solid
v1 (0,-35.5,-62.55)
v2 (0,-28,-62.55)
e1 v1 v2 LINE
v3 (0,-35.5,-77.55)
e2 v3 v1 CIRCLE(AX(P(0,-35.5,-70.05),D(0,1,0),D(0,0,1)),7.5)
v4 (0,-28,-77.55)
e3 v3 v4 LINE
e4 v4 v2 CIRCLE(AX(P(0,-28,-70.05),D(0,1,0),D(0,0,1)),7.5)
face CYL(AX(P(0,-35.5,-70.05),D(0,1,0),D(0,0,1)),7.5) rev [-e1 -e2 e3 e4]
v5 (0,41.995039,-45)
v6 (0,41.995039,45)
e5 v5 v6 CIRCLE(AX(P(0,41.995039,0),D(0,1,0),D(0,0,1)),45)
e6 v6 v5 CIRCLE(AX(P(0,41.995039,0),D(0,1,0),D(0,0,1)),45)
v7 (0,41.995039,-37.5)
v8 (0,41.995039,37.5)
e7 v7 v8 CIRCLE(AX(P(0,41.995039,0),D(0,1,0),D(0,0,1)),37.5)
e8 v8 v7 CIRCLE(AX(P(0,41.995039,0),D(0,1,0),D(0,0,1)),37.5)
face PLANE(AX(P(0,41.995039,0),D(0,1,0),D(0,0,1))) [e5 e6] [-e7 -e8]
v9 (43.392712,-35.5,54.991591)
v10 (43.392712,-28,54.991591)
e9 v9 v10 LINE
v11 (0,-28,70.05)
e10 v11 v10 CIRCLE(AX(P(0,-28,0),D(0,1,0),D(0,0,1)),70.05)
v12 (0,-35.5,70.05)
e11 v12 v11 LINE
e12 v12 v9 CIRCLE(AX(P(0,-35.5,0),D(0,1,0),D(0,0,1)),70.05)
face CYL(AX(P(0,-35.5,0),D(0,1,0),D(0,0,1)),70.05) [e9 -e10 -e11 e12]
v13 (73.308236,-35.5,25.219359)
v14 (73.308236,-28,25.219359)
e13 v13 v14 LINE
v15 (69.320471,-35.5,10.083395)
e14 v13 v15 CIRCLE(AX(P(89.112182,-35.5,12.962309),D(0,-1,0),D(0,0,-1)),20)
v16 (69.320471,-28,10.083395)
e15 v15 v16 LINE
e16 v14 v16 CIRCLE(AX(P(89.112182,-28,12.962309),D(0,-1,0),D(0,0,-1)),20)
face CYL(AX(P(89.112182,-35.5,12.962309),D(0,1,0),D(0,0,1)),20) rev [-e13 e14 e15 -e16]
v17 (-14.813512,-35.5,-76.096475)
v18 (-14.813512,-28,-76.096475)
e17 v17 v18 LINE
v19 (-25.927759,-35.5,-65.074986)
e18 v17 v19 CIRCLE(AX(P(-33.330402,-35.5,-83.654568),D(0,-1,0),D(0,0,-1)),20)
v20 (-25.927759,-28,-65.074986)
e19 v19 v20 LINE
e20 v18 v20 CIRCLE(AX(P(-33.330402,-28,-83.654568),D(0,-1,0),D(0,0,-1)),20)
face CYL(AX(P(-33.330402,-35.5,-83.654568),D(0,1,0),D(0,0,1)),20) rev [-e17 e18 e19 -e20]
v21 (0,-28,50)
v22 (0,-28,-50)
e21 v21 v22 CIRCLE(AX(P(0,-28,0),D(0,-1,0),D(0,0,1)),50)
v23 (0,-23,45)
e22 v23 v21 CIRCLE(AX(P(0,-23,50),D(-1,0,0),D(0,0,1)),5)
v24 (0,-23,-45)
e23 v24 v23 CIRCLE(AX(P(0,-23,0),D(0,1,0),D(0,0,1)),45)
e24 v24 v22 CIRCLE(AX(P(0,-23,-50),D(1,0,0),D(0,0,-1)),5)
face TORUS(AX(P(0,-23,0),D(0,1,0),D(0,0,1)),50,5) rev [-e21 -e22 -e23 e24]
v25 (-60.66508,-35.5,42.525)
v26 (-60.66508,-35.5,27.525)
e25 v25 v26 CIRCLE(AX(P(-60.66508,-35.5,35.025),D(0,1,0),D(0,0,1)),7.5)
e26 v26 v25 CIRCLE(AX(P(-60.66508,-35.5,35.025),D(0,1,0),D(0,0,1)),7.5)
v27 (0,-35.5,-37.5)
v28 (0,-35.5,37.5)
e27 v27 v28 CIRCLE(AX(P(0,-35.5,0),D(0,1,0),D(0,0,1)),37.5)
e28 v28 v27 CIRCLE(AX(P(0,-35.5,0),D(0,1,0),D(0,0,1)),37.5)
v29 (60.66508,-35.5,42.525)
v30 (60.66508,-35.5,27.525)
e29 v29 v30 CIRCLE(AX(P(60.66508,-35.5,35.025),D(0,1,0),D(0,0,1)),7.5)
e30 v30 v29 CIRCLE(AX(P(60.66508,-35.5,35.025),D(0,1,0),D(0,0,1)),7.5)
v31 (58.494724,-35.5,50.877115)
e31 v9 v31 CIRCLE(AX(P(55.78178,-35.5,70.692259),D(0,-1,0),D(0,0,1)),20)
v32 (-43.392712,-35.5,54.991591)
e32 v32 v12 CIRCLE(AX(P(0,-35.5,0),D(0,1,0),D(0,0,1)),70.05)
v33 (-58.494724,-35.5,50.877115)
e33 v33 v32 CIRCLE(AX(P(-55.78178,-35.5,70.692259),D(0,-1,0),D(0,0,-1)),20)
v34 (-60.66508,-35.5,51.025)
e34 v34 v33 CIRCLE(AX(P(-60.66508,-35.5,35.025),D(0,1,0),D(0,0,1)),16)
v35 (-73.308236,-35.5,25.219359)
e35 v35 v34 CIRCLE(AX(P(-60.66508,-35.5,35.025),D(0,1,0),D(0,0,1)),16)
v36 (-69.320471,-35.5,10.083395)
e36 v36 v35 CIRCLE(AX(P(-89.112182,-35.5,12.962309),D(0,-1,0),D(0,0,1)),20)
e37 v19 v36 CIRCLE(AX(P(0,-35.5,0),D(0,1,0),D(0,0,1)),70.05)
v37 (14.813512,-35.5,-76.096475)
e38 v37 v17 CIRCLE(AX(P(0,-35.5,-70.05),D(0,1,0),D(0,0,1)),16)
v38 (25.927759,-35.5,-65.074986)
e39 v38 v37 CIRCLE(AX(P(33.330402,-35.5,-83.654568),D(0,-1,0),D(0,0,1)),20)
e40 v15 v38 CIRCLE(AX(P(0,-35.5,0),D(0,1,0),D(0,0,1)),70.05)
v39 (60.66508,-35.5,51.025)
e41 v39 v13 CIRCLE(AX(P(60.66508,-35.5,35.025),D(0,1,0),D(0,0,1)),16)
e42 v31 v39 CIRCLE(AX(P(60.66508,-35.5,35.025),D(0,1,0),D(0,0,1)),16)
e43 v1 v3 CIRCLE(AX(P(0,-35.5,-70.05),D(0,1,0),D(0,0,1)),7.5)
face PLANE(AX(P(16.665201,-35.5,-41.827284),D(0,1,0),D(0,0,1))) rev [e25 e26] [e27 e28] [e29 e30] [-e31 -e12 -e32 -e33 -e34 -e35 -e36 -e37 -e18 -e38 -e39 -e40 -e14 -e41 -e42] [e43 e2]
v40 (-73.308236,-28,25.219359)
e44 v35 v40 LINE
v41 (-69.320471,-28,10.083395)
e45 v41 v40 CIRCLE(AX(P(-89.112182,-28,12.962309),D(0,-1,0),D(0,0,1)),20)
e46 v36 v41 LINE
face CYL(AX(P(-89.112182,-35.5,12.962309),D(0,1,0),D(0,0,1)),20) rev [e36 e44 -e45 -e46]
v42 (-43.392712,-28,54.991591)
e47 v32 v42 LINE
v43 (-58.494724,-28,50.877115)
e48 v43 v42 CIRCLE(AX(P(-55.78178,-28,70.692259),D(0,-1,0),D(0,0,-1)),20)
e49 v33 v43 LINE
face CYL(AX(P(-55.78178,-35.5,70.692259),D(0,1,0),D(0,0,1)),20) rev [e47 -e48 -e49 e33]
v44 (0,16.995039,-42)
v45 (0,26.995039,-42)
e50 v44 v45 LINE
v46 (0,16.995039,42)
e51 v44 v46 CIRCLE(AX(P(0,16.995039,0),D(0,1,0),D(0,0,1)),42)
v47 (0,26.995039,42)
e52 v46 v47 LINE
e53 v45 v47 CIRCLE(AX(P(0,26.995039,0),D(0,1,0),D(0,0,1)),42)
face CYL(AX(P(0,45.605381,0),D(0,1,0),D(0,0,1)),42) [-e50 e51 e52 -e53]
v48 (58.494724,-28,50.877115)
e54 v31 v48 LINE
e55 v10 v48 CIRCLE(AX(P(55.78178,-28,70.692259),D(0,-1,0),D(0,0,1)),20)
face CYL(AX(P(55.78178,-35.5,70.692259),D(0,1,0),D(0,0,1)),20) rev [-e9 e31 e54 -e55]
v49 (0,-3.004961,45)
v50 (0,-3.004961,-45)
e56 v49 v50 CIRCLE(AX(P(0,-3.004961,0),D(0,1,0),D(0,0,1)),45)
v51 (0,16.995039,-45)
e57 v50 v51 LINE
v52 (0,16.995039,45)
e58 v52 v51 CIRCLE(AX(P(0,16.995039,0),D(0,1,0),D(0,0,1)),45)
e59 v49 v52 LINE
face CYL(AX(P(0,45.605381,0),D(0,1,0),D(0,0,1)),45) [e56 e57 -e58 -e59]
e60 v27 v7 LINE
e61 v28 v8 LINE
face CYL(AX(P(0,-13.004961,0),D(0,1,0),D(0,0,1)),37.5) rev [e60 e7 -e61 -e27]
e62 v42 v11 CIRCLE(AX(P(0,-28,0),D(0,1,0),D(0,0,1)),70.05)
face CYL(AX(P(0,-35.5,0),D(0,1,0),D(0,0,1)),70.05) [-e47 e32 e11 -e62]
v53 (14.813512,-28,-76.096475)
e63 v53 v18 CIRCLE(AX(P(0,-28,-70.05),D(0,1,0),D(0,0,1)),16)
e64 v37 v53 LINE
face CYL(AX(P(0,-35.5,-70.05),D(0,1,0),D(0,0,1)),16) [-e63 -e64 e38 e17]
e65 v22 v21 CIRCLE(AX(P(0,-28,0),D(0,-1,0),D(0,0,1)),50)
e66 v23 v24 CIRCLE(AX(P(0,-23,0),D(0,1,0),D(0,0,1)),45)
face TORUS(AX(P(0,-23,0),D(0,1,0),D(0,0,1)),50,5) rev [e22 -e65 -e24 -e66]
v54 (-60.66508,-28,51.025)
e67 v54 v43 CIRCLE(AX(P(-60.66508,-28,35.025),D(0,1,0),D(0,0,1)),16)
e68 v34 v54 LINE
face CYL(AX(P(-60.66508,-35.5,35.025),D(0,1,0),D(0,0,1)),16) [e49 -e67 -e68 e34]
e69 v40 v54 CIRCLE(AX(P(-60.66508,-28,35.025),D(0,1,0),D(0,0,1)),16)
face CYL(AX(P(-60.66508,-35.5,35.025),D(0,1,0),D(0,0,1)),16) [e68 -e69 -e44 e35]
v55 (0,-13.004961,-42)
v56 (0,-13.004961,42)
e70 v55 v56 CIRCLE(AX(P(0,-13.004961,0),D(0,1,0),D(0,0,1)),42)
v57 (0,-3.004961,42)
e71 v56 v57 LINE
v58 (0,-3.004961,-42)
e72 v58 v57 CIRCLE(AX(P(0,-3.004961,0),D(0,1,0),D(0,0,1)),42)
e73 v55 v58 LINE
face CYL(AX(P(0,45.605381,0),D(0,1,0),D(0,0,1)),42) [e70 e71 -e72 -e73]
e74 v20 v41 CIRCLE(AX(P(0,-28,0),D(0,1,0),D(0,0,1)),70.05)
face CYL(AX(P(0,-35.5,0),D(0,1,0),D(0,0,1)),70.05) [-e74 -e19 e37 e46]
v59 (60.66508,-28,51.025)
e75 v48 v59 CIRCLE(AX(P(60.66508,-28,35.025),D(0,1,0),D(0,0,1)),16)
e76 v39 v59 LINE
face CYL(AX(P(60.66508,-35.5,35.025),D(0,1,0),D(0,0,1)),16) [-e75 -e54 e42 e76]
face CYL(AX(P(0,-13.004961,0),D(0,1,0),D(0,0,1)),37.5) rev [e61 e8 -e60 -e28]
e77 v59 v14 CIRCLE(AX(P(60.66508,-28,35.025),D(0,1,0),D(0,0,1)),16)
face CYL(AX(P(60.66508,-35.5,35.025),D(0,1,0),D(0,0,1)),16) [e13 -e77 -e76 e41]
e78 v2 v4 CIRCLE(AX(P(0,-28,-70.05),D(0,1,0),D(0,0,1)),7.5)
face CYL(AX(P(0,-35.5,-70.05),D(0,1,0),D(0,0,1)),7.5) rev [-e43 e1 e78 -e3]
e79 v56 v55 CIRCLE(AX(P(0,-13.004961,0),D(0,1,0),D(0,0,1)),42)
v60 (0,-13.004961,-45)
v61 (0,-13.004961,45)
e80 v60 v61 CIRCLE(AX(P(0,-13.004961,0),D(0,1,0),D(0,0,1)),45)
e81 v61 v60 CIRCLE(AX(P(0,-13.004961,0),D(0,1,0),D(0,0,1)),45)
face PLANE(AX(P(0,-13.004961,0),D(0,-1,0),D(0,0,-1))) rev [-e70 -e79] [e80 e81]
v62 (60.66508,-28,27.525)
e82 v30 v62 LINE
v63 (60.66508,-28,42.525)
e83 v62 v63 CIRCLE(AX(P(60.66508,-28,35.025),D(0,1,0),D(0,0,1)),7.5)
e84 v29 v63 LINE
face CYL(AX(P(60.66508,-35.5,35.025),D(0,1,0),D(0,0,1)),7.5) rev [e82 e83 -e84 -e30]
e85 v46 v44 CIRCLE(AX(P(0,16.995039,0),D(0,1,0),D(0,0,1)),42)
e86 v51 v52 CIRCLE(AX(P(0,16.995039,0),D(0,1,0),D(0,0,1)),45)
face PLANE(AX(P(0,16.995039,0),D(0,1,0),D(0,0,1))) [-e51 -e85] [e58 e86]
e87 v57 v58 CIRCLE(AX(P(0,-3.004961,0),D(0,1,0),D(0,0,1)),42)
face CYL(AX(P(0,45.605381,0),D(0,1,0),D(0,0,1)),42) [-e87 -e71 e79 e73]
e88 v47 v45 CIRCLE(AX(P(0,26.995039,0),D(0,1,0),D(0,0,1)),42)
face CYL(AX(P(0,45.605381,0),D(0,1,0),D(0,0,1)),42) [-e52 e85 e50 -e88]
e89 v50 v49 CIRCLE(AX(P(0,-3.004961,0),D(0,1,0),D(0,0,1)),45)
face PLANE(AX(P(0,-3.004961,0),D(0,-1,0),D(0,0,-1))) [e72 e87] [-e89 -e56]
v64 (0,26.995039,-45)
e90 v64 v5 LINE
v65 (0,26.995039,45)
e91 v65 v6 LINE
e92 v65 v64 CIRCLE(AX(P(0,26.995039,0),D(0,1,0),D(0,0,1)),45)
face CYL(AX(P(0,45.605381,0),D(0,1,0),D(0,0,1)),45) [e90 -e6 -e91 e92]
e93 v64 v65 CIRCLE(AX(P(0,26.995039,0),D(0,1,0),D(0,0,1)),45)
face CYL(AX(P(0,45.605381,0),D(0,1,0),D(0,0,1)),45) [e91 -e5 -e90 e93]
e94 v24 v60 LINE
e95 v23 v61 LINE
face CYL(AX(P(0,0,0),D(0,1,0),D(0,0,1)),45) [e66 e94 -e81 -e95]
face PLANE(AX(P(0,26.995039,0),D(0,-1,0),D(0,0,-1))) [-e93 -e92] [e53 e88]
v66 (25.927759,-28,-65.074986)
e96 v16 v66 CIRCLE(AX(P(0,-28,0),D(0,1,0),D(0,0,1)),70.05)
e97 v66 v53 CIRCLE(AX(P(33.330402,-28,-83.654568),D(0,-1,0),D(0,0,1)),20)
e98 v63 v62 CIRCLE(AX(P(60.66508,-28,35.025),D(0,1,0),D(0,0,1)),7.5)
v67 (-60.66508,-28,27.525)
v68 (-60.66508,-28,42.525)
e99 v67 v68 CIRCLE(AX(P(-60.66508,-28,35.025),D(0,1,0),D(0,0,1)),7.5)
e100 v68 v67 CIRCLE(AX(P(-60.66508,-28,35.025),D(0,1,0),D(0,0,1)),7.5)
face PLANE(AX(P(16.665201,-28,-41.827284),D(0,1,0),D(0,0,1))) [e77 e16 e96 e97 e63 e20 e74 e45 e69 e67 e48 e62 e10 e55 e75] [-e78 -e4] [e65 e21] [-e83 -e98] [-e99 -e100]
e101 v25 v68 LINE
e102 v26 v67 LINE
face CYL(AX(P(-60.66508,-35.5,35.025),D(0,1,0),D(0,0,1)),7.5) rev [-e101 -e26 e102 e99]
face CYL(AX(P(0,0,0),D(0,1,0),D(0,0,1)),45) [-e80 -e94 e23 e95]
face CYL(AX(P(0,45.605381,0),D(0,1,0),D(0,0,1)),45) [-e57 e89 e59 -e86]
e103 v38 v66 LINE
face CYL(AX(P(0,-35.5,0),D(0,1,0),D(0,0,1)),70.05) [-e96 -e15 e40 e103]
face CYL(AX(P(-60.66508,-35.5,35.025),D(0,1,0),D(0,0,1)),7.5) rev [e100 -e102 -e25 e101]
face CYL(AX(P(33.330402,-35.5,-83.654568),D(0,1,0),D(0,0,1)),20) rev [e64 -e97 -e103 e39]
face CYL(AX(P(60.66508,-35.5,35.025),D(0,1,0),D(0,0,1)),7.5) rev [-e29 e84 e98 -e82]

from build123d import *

# Parameters (mm, degrees)
CUT_CIRCLE_75_SKETCH_R        = 37.5
CUT_75_DEPTH                  = 85.113019206
MOUNTING_START                = -28
MOUNTING_FLANGE_SKETCH_R      = 7.5
MOUNTING_FLANGE_3_HOLES_DEPTH = 7.5
HUB_CUT_SKETCH_R              = 37.5
HUB_CUT_DEPTH                 = 139.879868922
HUB_FILLET_R5_R               = 5


with BuildPart() as part:
    # Spigot Profile Sketch → Spigot Body (revolve)
    with BuildSketch(Plane.XY, mode=Mode.PRIVATE) as spigot_body_sk:
        Polygon((0, -13.004960987), (0, 41.995039013), (-45, 41.995039013), (-45, 26.995039013), (-42, 26.995039013), (-42, 16.995039013), (-45, 16.995039013), (-45, -3.004960987), (-42, -3.004960987), (-42, -13.004960987), align=None)
    revolve(spigot_body_sk.sketch.rotate(Axis((0, 45.605381166, 0), (0, -1, 0)), 270), axis=Axis((0, 45.605381166, 0), (0, -1, 0)))

    # Cut Circle Ø75 Sketch → Cut Ø75 (cut, through all)
    with BuildSketch(Plane(origin=(0, 41.995039013, 0), x_dir=(1, 0, 0), z_dir=(0, 1, 0))):
        with Locations(Location((0, 0, 0), (0, 0, 270))):
            Circle(CUT_CIRCLE_75_SKETCH_R)
    extrude(amount=-CUT_75_DEPTH, mode=Mode.SUBTRACT)



with BuildPart() as body_2:
    # Mounting Flange Sketch → Mounting Flange 3 Holes (new body)
    with BuildSketch(Plane(origin=(0, 0, 0), x_dir=(1, 0, 0), z_dir=(0, 1, 0)).offset(MOUNTING_START)):
        with BuildLine():
            ThreePointArc((14.813512184, 76.09647474), (0, 86.05), (-14.813512184, 76.09647474))
            ThreePointArc((-14.813512184, 76.09647474), (-19.247651964, 69.453295695), (-25.927758901, 65.074986119))
            ThreePointArc((-25.927758901, 65.074986119), (-60.665079535, 35.025), (-69.32047058, -10.083395188))
            ThreePointArc((-69.32047058, -10.083395188), (-69.77214443, -18.057692283), (-73.308236355, -25.2193595))
            ThreePointArc((-73.308236355, -25.2193595), (-74.521485996, -43.025), (-58.494724172, -50.87711524))
            ThreePointArc((-58.494724172, -50.87711524), (-50.524492466, -51.395603412), (-43.392711679, -54.991590931))
            ThreePointArc((-43.392711679, -54.991590931), (0, -70.05), (43.392711679, -54.991590931))
            ThreePointArc((43.392711679, -54.991590931), (50.524492466, -51.395603412), (58.494724172, -50.87711524))
            ThreePointArc((58.494724172, -50.87711524), (74.521485996, -43.025), (73.308236355, -25.2193595))
            ThreePointArc((73.308236355, -25.2193595), (69.77214443, -18.057692283), (69.32047058, -10.083395188))
            ThreePointArc((69.32047058, -10.083395188), (60.665079535, 35.025), (25.927758901, 65.074986119))
            ThreePointArc((25.927758901, 65.074986119), (19.247651964, 69.453295695), (14.813512184, 76.09647474))
        make_face()
        with Locations(Location((0, 70.05, 0), (0, 0, 270))):
            Circle(MOUNTING_FLANGE_SKETCH_R, mode=Mode.SUBTRACT)
        with Locations(Location((60.665079535, -35.025, 0), (0, 0, 270))):
            Circle(MOUNTING_FLANGE_SKETCH_R, mode=Mode.SUBTRACT)
        with Locations(Location((-60.665079535, -35.025, 0), (0, 0, 270))):
            Circle(MOUNTING_FLANGE_SKETCH_R, mode=Mode.SUBTRACT)
    extrude(amount=-MOUNTING_FLANGE_3_HOLES_DEPTH)


with BuildPart() as part_1:
    add(part.part)

    add(body_2.part)  # Flange Hub merges body 2
    # Flange Hub Profile Sketch → Flange Hub (revolve)
    with BuildSketch(Plane.XY, mode=Mode.PRIVATE) as flange_hub_sk:
        Polygon((-45, -28), (0, -28), (0, -13.004960987), (-42, -13.004960987), (-45, -13.004960987), (-45, -23), align=None)
    revolve(flange_hub_sk.sketch.rotate(Axis((0, 0, 0), (0, -1, 0)), 270), axis=Axis((0, 0, 0), (0, -1, 0)))

    # Hub Cut Sketch → Hub Cut (cut, through all)
    with BuildSketch(Plane(origin=(0, 41.995039013, 0), x_dir=(1, 0, 0), z_dir=(0, 1, 0))):
        with Locations(Location((0, 0, 0), (0, 0, 270))):
            Circle(HUB_CUT_SKETCH_R)
    extrude(amount=-HUB_CUT_DEPTH, mode=Mode.SUBTRACT)

    # Hub Fillet R5
    hub_fillet_r5_edges = [part_1.edges().sort_by_distance(p)[0] for p in [
        (0, -28, -45),
    ]]
    fillet(hub_fillet_r5_edges, radius=HUB_FILLET_R5_R)


solid = part_1.part
